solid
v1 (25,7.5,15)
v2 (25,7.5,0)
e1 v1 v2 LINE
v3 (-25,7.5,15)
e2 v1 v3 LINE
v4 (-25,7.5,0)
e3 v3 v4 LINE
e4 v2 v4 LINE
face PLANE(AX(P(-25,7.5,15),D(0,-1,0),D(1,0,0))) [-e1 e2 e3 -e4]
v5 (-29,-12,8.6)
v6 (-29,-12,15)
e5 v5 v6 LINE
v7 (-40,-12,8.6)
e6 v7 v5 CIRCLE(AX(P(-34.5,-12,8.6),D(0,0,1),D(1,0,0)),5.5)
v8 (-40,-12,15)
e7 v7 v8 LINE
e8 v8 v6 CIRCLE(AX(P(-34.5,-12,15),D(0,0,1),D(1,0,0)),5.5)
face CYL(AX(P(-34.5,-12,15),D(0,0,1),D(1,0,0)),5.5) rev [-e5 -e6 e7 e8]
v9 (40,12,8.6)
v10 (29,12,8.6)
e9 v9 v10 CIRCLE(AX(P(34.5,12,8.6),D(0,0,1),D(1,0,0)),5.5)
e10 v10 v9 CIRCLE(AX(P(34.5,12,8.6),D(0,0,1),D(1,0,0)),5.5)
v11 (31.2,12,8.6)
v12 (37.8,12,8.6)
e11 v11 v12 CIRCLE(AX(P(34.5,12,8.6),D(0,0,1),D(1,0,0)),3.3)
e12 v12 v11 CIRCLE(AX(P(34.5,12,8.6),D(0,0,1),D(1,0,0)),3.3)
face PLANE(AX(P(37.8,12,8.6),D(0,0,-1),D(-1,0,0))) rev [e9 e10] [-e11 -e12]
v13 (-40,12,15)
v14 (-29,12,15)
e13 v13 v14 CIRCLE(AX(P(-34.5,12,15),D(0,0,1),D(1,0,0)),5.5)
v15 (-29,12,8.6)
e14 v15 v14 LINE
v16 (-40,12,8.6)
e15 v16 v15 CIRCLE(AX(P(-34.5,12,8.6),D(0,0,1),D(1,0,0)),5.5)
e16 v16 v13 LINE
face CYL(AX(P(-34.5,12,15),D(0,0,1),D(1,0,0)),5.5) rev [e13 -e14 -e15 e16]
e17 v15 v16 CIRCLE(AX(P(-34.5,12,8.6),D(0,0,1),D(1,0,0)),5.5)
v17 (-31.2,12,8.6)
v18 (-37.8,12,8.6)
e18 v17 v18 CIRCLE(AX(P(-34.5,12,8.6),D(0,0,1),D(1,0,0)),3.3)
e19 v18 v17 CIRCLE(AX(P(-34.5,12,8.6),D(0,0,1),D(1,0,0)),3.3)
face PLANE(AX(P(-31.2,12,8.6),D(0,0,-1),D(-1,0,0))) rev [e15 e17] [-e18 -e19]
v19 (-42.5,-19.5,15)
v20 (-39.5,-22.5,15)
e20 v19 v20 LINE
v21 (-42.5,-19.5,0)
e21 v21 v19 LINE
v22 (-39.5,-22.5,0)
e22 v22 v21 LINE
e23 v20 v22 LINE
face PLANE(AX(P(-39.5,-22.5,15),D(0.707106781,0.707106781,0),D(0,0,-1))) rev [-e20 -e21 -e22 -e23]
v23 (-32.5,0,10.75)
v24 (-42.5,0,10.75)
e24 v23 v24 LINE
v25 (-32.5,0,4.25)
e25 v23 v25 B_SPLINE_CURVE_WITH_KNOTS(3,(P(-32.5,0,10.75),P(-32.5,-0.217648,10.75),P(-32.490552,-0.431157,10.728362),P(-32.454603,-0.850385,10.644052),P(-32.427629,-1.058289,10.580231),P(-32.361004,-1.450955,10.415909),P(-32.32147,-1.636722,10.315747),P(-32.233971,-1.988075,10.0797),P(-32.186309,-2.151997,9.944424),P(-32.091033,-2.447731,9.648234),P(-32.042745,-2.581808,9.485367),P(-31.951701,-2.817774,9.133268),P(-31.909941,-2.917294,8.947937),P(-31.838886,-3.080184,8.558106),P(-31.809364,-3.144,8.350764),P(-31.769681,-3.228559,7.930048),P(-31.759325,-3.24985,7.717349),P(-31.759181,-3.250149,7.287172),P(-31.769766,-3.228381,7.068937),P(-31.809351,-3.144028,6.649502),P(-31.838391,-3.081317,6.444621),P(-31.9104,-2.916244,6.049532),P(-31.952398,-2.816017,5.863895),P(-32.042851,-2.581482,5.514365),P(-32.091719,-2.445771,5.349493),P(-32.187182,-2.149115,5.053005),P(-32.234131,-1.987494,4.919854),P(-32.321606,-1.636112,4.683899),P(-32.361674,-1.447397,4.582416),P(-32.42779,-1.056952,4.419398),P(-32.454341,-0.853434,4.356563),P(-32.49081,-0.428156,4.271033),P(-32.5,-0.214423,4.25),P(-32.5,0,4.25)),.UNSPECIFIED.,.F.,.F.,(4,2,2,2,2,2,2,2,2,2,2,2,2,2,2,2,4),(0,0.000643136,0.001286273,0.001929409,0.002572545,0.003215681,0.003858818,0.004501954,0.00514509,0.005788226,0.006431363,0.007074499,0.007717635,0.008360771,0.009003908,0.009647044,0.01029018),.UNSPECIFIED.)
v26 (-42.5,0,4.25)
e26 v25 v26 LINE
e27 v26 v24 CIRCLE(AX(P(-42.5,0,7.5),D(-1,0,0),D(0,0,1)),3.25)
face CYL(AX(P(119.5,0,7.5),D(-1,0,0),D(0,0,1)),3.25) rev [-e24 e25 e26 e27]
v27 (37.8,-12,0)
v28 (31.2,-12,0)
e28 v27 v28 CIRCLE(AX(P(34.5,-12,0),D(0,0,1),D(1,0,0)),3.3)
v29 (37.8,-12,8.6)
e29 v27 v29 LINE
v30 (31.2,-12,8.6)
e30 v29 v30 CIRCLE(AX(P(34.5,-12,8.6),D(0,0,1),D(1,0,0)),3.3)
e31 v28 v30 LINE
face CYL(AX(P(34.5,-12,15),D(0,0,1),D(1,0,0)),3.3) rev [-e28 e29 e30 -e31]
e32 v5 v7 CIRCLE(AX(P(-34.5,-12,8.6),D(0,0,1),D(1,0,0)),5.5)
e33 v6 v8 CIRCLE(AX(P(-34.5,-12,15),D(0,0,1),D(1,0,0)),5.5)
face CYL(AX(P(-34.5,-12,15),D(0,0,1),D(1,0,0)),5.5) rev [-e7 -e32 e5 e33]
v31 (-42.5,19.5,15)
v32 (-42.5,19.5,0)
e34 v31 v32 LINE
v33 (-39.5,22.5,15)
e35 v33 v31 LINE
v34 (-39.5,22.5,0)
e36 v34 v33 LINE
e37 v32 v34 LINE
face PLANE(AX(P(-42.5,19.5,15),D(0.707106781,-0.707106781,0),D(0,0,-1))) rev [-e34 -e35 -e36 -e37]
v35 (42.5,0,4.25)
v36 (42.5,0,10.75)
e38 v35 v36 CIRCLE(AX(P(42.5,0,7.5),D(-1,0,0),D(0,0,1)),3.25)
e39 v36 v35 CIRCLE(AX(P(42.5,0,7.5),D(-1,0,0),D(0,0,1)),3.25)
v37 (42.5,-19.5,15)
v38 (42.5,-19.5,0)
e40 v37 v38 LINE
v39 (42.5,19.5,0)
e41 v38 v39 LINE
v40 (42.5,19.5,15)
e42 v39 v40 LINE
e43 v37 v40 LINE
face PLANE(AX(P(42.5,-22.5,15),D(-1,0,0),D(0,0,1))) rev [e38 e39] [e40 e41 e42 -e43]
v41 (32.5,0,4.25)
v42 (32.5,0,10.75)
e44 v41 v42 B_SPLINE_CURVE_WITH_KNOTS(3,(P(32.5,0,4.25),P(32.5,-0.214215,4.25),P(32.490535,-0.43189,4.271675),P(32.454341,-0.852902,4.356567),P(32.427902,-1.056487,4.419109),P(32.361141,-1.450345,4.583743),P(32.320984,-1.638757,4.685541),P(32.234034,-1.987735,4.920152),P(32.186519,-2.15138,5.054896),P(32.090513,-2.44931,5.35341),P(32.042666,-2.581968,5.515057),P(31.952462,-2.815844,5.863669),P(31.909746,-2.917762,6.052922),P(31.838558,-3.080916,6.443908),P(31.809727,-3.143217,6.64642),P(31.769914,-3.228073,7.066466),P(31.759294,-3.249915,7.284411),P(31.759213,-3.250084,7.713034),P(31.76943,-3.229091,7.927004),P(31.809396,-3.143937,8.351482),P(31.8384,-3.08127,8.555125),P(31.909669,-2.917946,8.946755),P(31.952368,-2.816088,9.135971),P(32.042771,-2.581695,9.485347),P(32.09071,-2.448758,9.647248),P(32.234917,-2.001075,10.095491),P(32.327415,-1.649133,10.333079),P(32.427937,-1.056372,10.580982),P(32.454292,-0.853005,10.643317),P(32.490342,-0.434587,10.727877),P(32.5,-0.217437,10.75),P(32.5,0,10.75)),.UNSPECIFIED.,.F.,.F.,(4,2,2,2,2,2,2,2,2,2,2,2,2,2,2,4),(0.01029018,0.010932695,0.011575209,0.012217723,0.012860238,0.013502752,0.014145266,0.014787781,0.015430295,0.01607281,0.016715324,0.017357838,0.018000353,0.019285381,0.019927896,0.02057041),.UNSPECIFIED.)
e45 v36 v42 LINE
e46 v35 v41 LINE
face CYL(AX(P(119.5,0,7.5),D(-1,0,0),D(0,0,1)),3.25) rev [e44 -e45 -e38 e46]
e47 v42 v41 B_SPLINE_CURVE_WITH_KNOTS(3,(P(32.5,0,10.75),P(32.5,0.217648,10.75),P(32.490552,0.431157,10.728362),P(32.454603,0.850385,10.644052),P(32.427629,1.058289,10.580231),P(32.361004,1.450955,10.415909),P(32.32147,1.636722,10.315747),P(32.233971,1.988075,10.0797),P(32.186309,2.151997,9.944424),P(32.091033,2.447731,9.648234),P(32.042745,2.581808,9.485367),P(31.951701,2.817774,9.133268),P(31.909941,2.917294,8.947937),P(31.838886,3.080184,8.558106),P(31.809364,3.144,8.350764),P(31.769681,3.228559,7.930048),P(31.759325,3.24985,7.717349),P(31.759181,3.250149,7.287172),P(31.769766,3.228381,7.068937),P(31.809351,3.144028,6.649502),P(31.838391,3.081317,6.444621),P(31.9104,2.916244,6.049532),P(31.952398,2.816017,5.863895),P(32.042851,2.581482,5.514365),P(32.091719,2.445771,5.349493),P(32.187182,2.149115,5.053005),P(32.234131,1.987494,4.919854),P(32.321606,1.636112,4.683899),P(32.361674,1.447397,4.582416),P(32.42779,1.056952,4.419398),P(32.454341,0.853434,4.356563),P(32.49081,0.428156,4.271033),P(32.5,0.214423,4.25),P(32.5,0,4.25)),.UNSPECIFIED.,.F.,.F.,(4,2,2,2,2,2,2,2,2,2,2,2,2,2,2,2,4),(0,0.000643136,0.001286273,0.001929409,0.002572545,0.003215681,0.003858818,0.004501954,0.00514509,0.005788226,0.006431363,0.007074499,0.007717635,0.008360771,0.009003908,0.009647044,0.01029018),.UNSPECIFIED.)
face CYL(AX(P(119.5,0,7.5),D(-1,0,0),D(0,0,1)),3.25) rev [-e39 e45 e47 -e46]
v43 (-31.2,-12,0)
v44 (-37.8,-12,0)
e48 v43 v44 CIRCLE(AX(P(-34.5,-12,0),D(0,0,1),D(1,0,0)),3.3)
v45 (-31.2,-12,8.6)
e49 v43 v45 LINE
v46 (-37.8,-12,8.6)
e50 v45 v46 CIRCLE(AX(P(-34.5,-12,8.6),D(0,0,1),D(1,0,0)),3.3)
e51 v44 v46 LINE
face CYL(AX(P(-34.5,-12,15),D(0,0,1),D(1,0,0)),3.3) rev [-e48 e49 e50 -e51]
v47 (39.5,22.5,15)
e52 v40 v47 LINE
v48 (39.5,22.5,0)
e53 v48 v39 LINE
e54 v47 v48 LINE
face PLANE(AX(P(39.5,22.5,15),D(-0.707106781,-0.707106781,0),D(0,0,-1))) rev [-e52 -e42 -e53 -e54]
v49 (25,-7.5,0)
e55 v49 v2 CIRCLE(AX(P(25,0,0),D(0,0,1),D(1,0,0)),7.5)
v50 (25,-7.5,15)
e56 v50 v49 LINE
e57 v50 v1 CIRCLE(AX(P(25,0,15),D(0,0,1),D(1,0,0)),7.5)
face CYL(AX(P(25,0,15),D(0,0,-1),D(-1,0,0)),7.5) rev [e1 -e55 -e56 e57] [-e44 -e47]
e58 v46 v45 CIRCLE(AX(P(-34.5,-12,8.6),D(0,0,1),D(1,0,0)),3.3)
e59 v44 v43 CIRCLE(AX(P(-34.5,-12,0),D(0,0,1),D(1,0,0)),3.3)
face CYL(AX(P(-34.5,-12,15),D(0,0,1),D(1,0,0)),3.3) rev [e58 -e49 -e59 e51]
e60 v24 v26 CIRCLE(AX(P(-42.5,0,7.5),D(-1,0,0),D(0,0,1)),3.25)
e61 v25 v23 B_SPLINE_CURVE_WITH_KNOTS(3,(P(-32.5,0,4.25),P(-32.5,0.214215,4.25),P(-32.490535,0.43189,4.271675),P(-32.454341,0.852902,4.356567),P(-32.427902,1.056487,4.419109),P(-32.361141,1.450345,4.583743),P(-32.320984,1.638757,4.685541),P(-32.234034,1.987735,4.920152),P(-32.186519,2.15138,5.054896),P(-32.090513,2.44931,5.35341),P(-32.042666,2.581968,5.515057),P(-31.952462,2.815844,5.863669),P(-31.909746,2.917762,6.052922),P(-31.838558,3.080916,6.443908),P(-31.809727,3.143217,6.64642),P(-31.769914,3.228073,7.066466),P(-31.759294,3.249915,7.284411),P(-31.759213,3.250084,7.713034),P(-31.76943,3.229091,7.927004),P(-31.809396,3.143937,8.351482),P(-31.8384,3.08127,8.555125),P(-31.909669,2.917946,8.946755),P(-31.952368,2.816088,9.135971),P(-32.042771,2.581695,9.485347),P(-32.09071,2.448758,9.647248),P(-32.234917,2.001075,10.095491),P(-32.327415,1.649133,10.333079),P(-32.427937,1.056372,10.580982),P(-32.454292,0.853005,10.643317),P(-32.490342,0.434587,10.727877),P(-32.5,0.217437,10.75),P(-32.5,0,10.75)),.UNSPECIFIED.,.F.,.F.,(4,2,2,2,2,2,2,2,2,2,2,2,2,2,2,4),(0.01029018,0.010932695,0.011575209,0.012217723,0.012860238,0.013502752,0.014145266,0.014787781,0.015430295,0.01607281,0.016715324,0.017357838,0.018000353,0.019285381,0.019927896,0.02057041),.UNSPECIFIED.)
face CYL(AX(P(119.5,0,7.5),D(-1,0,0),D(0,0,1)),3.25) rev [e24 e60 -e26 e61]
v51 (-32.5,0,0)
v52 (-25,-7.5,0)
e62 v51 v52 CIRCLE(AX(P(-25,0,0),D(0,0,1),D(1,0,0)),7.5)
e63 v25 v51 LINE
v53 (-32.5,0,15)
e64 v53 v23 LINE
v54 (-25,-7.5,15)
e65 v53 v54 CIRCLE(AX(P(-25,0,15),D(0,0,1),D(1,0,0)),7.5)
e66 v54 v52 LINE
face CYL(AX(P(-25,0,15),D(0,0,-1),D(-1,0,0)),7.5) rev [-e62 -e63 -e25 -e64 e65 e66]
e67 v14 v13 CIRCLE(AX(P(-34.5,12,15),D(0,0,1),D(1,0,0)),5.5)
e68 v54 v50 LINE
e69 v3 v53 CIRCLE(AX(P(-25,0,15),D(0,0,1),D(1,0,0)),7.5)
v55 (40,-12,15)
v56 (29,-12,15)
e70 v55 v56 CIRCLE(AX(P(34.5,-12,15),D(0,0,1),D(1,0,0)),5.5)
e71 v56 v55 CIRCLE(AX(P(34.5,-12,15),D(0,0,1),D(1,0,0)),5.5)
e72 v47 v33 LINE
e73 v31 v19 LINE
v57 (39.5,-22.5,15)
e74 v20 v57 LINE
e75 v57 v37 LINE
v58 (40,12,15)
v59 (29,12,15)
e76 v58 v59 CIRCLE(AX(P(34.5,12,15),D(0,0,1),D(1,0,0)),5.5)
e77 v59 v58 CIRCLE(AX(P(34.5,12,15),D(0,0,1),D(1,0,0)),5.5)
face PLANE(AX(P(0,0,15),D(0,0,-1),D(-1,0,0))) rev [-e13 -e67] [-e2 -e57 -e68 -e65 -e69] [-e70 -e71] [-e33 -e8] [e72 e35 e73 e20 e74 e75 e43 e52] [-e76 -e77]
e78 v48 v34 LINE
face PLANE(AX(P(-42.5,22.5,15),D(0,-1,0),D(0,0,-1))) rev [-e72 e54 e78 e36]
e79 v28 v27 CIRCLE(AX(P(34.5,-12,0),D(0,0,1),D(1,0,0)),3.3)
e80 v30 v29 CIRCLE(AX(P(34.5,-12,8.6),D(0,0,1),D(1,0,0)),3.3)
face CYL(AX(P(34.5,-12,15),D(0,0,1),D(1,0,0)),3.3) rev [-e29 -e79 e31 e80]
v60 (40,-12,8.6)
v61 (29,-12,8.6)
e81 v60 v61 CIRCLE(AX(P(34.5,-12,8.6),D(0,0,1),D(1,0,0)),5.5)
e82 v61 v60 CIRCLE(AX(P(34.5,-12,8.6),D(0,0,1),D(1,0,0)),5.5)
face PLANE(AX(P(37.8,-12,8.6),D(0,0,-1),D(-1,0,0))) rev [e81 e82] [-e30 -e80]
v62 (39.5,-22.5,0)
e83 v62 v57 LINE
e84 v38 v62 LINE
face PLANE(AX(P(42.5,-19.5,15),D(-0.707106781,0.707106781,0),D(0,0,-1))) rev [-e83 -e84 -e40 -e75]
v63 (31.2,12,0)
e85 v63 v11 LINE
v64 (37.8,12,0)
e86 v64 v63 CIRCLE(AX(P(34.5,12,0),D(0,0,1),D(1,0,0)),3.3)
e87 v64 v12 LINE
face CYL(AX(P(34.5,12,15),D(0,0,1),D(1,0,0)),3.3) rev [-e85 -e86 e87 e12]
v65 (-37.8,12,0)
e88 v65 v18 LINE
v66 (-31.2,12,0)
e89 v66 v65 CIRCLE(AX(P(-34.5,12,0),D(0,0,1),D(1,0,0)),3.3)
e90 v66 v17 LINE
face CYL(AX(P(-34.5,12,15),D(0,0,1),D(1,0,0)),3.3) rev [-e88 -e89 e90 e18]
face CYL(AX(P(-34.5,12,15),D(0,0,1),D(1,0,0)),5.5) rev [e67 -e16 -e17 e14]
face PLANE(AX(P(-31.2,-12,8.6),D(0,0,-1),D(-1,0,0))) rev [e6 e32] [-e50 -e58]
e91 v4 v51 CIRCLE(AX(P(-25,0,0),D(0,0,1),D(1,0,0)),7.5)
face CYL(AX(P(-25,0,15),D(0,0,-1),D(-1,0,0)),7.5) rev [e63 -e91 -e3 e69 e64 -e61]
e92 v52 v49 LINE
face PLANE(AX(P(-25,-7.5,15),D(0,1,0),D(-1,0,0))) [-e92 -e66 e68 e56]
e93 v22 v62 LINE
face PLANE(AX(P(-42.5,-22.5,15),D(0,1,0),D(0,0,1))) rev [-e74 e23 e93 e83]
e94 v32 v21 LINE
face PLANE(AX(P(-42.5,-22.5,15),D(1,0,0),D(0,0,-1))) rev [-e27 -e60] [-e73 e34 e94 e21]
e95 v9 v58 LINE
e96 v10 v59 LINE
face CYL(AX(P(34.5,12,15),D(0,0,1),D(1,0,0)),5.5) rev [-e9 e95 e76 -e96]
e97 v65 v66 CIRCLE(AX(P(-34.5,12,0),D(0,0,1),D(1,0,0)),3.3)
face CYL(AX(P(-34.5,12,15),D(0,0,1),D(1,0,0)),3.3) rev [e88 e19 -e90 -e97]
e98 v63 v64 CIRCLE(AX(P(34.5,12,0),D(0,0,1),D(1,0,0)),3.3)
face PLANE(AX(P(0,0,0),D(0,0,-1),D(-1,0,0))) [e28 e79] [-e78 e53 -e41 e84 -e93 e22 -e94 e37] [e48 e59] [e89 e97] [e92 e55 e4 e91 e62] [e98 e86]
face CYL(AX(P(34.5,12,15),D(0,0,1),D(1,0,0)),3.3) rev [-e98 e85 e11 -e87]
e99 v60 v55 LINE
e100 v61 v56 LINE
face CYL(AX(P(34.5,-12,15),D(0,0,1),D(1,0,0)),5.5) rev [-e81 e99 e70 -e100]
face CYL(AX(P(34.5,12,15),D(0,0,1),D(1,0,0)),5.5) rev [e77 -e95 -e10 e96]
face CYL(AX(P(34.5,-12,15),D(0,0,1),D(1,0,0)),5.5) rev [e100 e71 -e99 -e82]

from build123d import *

# Parameters (mm, degrees)
SKETCH_1_W                   = 85
SKETCH_1_H                   = 45
EXTRUDE_1_DEPTH              = 15
HOLE_WIZARD_M6_1_D           = 6.6
HOLE_WIZARD_M6_1_CBORE_D     = 11
HOLE_WIZARD_M6_1_CBORE_DEPTH = 6.4
SKETCH_4_R                   = 3.25
CUT_EXTRUDE_1_DEPTH          = 162
CHAMFER_1_SIZE               = 3


with BuildPart() as part:
    # 草图1 → 凸台-拉伸1 (new body)
    with BuildSketch(Plane.XY):
        Rectangle(SKETCH_1_W, SKETCH_1_H)
        with BuildLine():
            Line((-25, 7.5), (25, 7.5))
            ThreePointArc((25, 7.5), (32.5, 0), (25, -7.5))
            Line((25, -7.5), (-25, -7.5))
            ThreePointArc((-25, -7.5), (-32.5, 0), (-25, 7.5))
        make_face(mode=Mode.SUBTRACT)
    extrude(amount=EXTRUDE_1_DEPTH)

    # M6 六角凹头螺钉的柱形沉头孔1 (through all)
    with Locations(Plane.XY.offset(15)):
        with Locations((-34.5, 12), (-34.5, -12), (34.5, -12), (34.5, 12)):
            CounterBoreHole(HOLE_WIZARD_M6_1_D / 2, HOLE_WIZARD_M6_1_CBORE_D / 2, HOLE_WIZARD_M6_1_CBORE_DEPTH)

    # 草图4 → 切除-拉伸1 (cut)
    with BuildSketch(Plane.ZY.offset(42.5)):
        with Locations((7.5, 0)):
            Circle(SKETCH_4_R)
    extrude(amount=-CUT_EXTRUDE_1_DEPTH, mode=Mode.SUBTRACT)

    # 倒角1
    chamfer_1_edges = [part.edges().sort_by_distance(p)[0] for p in [
        (42.5, -22.5, 7.5),
        (-42.5, -22.5, 7.5),
        (-42.5, 22.5, 7.5),
        (42.5, 22.5, 7.5),
    ]]
    chamfer(chamfer_1_edges, length=CHAMFER_1_SIZE)


solid = part.part
